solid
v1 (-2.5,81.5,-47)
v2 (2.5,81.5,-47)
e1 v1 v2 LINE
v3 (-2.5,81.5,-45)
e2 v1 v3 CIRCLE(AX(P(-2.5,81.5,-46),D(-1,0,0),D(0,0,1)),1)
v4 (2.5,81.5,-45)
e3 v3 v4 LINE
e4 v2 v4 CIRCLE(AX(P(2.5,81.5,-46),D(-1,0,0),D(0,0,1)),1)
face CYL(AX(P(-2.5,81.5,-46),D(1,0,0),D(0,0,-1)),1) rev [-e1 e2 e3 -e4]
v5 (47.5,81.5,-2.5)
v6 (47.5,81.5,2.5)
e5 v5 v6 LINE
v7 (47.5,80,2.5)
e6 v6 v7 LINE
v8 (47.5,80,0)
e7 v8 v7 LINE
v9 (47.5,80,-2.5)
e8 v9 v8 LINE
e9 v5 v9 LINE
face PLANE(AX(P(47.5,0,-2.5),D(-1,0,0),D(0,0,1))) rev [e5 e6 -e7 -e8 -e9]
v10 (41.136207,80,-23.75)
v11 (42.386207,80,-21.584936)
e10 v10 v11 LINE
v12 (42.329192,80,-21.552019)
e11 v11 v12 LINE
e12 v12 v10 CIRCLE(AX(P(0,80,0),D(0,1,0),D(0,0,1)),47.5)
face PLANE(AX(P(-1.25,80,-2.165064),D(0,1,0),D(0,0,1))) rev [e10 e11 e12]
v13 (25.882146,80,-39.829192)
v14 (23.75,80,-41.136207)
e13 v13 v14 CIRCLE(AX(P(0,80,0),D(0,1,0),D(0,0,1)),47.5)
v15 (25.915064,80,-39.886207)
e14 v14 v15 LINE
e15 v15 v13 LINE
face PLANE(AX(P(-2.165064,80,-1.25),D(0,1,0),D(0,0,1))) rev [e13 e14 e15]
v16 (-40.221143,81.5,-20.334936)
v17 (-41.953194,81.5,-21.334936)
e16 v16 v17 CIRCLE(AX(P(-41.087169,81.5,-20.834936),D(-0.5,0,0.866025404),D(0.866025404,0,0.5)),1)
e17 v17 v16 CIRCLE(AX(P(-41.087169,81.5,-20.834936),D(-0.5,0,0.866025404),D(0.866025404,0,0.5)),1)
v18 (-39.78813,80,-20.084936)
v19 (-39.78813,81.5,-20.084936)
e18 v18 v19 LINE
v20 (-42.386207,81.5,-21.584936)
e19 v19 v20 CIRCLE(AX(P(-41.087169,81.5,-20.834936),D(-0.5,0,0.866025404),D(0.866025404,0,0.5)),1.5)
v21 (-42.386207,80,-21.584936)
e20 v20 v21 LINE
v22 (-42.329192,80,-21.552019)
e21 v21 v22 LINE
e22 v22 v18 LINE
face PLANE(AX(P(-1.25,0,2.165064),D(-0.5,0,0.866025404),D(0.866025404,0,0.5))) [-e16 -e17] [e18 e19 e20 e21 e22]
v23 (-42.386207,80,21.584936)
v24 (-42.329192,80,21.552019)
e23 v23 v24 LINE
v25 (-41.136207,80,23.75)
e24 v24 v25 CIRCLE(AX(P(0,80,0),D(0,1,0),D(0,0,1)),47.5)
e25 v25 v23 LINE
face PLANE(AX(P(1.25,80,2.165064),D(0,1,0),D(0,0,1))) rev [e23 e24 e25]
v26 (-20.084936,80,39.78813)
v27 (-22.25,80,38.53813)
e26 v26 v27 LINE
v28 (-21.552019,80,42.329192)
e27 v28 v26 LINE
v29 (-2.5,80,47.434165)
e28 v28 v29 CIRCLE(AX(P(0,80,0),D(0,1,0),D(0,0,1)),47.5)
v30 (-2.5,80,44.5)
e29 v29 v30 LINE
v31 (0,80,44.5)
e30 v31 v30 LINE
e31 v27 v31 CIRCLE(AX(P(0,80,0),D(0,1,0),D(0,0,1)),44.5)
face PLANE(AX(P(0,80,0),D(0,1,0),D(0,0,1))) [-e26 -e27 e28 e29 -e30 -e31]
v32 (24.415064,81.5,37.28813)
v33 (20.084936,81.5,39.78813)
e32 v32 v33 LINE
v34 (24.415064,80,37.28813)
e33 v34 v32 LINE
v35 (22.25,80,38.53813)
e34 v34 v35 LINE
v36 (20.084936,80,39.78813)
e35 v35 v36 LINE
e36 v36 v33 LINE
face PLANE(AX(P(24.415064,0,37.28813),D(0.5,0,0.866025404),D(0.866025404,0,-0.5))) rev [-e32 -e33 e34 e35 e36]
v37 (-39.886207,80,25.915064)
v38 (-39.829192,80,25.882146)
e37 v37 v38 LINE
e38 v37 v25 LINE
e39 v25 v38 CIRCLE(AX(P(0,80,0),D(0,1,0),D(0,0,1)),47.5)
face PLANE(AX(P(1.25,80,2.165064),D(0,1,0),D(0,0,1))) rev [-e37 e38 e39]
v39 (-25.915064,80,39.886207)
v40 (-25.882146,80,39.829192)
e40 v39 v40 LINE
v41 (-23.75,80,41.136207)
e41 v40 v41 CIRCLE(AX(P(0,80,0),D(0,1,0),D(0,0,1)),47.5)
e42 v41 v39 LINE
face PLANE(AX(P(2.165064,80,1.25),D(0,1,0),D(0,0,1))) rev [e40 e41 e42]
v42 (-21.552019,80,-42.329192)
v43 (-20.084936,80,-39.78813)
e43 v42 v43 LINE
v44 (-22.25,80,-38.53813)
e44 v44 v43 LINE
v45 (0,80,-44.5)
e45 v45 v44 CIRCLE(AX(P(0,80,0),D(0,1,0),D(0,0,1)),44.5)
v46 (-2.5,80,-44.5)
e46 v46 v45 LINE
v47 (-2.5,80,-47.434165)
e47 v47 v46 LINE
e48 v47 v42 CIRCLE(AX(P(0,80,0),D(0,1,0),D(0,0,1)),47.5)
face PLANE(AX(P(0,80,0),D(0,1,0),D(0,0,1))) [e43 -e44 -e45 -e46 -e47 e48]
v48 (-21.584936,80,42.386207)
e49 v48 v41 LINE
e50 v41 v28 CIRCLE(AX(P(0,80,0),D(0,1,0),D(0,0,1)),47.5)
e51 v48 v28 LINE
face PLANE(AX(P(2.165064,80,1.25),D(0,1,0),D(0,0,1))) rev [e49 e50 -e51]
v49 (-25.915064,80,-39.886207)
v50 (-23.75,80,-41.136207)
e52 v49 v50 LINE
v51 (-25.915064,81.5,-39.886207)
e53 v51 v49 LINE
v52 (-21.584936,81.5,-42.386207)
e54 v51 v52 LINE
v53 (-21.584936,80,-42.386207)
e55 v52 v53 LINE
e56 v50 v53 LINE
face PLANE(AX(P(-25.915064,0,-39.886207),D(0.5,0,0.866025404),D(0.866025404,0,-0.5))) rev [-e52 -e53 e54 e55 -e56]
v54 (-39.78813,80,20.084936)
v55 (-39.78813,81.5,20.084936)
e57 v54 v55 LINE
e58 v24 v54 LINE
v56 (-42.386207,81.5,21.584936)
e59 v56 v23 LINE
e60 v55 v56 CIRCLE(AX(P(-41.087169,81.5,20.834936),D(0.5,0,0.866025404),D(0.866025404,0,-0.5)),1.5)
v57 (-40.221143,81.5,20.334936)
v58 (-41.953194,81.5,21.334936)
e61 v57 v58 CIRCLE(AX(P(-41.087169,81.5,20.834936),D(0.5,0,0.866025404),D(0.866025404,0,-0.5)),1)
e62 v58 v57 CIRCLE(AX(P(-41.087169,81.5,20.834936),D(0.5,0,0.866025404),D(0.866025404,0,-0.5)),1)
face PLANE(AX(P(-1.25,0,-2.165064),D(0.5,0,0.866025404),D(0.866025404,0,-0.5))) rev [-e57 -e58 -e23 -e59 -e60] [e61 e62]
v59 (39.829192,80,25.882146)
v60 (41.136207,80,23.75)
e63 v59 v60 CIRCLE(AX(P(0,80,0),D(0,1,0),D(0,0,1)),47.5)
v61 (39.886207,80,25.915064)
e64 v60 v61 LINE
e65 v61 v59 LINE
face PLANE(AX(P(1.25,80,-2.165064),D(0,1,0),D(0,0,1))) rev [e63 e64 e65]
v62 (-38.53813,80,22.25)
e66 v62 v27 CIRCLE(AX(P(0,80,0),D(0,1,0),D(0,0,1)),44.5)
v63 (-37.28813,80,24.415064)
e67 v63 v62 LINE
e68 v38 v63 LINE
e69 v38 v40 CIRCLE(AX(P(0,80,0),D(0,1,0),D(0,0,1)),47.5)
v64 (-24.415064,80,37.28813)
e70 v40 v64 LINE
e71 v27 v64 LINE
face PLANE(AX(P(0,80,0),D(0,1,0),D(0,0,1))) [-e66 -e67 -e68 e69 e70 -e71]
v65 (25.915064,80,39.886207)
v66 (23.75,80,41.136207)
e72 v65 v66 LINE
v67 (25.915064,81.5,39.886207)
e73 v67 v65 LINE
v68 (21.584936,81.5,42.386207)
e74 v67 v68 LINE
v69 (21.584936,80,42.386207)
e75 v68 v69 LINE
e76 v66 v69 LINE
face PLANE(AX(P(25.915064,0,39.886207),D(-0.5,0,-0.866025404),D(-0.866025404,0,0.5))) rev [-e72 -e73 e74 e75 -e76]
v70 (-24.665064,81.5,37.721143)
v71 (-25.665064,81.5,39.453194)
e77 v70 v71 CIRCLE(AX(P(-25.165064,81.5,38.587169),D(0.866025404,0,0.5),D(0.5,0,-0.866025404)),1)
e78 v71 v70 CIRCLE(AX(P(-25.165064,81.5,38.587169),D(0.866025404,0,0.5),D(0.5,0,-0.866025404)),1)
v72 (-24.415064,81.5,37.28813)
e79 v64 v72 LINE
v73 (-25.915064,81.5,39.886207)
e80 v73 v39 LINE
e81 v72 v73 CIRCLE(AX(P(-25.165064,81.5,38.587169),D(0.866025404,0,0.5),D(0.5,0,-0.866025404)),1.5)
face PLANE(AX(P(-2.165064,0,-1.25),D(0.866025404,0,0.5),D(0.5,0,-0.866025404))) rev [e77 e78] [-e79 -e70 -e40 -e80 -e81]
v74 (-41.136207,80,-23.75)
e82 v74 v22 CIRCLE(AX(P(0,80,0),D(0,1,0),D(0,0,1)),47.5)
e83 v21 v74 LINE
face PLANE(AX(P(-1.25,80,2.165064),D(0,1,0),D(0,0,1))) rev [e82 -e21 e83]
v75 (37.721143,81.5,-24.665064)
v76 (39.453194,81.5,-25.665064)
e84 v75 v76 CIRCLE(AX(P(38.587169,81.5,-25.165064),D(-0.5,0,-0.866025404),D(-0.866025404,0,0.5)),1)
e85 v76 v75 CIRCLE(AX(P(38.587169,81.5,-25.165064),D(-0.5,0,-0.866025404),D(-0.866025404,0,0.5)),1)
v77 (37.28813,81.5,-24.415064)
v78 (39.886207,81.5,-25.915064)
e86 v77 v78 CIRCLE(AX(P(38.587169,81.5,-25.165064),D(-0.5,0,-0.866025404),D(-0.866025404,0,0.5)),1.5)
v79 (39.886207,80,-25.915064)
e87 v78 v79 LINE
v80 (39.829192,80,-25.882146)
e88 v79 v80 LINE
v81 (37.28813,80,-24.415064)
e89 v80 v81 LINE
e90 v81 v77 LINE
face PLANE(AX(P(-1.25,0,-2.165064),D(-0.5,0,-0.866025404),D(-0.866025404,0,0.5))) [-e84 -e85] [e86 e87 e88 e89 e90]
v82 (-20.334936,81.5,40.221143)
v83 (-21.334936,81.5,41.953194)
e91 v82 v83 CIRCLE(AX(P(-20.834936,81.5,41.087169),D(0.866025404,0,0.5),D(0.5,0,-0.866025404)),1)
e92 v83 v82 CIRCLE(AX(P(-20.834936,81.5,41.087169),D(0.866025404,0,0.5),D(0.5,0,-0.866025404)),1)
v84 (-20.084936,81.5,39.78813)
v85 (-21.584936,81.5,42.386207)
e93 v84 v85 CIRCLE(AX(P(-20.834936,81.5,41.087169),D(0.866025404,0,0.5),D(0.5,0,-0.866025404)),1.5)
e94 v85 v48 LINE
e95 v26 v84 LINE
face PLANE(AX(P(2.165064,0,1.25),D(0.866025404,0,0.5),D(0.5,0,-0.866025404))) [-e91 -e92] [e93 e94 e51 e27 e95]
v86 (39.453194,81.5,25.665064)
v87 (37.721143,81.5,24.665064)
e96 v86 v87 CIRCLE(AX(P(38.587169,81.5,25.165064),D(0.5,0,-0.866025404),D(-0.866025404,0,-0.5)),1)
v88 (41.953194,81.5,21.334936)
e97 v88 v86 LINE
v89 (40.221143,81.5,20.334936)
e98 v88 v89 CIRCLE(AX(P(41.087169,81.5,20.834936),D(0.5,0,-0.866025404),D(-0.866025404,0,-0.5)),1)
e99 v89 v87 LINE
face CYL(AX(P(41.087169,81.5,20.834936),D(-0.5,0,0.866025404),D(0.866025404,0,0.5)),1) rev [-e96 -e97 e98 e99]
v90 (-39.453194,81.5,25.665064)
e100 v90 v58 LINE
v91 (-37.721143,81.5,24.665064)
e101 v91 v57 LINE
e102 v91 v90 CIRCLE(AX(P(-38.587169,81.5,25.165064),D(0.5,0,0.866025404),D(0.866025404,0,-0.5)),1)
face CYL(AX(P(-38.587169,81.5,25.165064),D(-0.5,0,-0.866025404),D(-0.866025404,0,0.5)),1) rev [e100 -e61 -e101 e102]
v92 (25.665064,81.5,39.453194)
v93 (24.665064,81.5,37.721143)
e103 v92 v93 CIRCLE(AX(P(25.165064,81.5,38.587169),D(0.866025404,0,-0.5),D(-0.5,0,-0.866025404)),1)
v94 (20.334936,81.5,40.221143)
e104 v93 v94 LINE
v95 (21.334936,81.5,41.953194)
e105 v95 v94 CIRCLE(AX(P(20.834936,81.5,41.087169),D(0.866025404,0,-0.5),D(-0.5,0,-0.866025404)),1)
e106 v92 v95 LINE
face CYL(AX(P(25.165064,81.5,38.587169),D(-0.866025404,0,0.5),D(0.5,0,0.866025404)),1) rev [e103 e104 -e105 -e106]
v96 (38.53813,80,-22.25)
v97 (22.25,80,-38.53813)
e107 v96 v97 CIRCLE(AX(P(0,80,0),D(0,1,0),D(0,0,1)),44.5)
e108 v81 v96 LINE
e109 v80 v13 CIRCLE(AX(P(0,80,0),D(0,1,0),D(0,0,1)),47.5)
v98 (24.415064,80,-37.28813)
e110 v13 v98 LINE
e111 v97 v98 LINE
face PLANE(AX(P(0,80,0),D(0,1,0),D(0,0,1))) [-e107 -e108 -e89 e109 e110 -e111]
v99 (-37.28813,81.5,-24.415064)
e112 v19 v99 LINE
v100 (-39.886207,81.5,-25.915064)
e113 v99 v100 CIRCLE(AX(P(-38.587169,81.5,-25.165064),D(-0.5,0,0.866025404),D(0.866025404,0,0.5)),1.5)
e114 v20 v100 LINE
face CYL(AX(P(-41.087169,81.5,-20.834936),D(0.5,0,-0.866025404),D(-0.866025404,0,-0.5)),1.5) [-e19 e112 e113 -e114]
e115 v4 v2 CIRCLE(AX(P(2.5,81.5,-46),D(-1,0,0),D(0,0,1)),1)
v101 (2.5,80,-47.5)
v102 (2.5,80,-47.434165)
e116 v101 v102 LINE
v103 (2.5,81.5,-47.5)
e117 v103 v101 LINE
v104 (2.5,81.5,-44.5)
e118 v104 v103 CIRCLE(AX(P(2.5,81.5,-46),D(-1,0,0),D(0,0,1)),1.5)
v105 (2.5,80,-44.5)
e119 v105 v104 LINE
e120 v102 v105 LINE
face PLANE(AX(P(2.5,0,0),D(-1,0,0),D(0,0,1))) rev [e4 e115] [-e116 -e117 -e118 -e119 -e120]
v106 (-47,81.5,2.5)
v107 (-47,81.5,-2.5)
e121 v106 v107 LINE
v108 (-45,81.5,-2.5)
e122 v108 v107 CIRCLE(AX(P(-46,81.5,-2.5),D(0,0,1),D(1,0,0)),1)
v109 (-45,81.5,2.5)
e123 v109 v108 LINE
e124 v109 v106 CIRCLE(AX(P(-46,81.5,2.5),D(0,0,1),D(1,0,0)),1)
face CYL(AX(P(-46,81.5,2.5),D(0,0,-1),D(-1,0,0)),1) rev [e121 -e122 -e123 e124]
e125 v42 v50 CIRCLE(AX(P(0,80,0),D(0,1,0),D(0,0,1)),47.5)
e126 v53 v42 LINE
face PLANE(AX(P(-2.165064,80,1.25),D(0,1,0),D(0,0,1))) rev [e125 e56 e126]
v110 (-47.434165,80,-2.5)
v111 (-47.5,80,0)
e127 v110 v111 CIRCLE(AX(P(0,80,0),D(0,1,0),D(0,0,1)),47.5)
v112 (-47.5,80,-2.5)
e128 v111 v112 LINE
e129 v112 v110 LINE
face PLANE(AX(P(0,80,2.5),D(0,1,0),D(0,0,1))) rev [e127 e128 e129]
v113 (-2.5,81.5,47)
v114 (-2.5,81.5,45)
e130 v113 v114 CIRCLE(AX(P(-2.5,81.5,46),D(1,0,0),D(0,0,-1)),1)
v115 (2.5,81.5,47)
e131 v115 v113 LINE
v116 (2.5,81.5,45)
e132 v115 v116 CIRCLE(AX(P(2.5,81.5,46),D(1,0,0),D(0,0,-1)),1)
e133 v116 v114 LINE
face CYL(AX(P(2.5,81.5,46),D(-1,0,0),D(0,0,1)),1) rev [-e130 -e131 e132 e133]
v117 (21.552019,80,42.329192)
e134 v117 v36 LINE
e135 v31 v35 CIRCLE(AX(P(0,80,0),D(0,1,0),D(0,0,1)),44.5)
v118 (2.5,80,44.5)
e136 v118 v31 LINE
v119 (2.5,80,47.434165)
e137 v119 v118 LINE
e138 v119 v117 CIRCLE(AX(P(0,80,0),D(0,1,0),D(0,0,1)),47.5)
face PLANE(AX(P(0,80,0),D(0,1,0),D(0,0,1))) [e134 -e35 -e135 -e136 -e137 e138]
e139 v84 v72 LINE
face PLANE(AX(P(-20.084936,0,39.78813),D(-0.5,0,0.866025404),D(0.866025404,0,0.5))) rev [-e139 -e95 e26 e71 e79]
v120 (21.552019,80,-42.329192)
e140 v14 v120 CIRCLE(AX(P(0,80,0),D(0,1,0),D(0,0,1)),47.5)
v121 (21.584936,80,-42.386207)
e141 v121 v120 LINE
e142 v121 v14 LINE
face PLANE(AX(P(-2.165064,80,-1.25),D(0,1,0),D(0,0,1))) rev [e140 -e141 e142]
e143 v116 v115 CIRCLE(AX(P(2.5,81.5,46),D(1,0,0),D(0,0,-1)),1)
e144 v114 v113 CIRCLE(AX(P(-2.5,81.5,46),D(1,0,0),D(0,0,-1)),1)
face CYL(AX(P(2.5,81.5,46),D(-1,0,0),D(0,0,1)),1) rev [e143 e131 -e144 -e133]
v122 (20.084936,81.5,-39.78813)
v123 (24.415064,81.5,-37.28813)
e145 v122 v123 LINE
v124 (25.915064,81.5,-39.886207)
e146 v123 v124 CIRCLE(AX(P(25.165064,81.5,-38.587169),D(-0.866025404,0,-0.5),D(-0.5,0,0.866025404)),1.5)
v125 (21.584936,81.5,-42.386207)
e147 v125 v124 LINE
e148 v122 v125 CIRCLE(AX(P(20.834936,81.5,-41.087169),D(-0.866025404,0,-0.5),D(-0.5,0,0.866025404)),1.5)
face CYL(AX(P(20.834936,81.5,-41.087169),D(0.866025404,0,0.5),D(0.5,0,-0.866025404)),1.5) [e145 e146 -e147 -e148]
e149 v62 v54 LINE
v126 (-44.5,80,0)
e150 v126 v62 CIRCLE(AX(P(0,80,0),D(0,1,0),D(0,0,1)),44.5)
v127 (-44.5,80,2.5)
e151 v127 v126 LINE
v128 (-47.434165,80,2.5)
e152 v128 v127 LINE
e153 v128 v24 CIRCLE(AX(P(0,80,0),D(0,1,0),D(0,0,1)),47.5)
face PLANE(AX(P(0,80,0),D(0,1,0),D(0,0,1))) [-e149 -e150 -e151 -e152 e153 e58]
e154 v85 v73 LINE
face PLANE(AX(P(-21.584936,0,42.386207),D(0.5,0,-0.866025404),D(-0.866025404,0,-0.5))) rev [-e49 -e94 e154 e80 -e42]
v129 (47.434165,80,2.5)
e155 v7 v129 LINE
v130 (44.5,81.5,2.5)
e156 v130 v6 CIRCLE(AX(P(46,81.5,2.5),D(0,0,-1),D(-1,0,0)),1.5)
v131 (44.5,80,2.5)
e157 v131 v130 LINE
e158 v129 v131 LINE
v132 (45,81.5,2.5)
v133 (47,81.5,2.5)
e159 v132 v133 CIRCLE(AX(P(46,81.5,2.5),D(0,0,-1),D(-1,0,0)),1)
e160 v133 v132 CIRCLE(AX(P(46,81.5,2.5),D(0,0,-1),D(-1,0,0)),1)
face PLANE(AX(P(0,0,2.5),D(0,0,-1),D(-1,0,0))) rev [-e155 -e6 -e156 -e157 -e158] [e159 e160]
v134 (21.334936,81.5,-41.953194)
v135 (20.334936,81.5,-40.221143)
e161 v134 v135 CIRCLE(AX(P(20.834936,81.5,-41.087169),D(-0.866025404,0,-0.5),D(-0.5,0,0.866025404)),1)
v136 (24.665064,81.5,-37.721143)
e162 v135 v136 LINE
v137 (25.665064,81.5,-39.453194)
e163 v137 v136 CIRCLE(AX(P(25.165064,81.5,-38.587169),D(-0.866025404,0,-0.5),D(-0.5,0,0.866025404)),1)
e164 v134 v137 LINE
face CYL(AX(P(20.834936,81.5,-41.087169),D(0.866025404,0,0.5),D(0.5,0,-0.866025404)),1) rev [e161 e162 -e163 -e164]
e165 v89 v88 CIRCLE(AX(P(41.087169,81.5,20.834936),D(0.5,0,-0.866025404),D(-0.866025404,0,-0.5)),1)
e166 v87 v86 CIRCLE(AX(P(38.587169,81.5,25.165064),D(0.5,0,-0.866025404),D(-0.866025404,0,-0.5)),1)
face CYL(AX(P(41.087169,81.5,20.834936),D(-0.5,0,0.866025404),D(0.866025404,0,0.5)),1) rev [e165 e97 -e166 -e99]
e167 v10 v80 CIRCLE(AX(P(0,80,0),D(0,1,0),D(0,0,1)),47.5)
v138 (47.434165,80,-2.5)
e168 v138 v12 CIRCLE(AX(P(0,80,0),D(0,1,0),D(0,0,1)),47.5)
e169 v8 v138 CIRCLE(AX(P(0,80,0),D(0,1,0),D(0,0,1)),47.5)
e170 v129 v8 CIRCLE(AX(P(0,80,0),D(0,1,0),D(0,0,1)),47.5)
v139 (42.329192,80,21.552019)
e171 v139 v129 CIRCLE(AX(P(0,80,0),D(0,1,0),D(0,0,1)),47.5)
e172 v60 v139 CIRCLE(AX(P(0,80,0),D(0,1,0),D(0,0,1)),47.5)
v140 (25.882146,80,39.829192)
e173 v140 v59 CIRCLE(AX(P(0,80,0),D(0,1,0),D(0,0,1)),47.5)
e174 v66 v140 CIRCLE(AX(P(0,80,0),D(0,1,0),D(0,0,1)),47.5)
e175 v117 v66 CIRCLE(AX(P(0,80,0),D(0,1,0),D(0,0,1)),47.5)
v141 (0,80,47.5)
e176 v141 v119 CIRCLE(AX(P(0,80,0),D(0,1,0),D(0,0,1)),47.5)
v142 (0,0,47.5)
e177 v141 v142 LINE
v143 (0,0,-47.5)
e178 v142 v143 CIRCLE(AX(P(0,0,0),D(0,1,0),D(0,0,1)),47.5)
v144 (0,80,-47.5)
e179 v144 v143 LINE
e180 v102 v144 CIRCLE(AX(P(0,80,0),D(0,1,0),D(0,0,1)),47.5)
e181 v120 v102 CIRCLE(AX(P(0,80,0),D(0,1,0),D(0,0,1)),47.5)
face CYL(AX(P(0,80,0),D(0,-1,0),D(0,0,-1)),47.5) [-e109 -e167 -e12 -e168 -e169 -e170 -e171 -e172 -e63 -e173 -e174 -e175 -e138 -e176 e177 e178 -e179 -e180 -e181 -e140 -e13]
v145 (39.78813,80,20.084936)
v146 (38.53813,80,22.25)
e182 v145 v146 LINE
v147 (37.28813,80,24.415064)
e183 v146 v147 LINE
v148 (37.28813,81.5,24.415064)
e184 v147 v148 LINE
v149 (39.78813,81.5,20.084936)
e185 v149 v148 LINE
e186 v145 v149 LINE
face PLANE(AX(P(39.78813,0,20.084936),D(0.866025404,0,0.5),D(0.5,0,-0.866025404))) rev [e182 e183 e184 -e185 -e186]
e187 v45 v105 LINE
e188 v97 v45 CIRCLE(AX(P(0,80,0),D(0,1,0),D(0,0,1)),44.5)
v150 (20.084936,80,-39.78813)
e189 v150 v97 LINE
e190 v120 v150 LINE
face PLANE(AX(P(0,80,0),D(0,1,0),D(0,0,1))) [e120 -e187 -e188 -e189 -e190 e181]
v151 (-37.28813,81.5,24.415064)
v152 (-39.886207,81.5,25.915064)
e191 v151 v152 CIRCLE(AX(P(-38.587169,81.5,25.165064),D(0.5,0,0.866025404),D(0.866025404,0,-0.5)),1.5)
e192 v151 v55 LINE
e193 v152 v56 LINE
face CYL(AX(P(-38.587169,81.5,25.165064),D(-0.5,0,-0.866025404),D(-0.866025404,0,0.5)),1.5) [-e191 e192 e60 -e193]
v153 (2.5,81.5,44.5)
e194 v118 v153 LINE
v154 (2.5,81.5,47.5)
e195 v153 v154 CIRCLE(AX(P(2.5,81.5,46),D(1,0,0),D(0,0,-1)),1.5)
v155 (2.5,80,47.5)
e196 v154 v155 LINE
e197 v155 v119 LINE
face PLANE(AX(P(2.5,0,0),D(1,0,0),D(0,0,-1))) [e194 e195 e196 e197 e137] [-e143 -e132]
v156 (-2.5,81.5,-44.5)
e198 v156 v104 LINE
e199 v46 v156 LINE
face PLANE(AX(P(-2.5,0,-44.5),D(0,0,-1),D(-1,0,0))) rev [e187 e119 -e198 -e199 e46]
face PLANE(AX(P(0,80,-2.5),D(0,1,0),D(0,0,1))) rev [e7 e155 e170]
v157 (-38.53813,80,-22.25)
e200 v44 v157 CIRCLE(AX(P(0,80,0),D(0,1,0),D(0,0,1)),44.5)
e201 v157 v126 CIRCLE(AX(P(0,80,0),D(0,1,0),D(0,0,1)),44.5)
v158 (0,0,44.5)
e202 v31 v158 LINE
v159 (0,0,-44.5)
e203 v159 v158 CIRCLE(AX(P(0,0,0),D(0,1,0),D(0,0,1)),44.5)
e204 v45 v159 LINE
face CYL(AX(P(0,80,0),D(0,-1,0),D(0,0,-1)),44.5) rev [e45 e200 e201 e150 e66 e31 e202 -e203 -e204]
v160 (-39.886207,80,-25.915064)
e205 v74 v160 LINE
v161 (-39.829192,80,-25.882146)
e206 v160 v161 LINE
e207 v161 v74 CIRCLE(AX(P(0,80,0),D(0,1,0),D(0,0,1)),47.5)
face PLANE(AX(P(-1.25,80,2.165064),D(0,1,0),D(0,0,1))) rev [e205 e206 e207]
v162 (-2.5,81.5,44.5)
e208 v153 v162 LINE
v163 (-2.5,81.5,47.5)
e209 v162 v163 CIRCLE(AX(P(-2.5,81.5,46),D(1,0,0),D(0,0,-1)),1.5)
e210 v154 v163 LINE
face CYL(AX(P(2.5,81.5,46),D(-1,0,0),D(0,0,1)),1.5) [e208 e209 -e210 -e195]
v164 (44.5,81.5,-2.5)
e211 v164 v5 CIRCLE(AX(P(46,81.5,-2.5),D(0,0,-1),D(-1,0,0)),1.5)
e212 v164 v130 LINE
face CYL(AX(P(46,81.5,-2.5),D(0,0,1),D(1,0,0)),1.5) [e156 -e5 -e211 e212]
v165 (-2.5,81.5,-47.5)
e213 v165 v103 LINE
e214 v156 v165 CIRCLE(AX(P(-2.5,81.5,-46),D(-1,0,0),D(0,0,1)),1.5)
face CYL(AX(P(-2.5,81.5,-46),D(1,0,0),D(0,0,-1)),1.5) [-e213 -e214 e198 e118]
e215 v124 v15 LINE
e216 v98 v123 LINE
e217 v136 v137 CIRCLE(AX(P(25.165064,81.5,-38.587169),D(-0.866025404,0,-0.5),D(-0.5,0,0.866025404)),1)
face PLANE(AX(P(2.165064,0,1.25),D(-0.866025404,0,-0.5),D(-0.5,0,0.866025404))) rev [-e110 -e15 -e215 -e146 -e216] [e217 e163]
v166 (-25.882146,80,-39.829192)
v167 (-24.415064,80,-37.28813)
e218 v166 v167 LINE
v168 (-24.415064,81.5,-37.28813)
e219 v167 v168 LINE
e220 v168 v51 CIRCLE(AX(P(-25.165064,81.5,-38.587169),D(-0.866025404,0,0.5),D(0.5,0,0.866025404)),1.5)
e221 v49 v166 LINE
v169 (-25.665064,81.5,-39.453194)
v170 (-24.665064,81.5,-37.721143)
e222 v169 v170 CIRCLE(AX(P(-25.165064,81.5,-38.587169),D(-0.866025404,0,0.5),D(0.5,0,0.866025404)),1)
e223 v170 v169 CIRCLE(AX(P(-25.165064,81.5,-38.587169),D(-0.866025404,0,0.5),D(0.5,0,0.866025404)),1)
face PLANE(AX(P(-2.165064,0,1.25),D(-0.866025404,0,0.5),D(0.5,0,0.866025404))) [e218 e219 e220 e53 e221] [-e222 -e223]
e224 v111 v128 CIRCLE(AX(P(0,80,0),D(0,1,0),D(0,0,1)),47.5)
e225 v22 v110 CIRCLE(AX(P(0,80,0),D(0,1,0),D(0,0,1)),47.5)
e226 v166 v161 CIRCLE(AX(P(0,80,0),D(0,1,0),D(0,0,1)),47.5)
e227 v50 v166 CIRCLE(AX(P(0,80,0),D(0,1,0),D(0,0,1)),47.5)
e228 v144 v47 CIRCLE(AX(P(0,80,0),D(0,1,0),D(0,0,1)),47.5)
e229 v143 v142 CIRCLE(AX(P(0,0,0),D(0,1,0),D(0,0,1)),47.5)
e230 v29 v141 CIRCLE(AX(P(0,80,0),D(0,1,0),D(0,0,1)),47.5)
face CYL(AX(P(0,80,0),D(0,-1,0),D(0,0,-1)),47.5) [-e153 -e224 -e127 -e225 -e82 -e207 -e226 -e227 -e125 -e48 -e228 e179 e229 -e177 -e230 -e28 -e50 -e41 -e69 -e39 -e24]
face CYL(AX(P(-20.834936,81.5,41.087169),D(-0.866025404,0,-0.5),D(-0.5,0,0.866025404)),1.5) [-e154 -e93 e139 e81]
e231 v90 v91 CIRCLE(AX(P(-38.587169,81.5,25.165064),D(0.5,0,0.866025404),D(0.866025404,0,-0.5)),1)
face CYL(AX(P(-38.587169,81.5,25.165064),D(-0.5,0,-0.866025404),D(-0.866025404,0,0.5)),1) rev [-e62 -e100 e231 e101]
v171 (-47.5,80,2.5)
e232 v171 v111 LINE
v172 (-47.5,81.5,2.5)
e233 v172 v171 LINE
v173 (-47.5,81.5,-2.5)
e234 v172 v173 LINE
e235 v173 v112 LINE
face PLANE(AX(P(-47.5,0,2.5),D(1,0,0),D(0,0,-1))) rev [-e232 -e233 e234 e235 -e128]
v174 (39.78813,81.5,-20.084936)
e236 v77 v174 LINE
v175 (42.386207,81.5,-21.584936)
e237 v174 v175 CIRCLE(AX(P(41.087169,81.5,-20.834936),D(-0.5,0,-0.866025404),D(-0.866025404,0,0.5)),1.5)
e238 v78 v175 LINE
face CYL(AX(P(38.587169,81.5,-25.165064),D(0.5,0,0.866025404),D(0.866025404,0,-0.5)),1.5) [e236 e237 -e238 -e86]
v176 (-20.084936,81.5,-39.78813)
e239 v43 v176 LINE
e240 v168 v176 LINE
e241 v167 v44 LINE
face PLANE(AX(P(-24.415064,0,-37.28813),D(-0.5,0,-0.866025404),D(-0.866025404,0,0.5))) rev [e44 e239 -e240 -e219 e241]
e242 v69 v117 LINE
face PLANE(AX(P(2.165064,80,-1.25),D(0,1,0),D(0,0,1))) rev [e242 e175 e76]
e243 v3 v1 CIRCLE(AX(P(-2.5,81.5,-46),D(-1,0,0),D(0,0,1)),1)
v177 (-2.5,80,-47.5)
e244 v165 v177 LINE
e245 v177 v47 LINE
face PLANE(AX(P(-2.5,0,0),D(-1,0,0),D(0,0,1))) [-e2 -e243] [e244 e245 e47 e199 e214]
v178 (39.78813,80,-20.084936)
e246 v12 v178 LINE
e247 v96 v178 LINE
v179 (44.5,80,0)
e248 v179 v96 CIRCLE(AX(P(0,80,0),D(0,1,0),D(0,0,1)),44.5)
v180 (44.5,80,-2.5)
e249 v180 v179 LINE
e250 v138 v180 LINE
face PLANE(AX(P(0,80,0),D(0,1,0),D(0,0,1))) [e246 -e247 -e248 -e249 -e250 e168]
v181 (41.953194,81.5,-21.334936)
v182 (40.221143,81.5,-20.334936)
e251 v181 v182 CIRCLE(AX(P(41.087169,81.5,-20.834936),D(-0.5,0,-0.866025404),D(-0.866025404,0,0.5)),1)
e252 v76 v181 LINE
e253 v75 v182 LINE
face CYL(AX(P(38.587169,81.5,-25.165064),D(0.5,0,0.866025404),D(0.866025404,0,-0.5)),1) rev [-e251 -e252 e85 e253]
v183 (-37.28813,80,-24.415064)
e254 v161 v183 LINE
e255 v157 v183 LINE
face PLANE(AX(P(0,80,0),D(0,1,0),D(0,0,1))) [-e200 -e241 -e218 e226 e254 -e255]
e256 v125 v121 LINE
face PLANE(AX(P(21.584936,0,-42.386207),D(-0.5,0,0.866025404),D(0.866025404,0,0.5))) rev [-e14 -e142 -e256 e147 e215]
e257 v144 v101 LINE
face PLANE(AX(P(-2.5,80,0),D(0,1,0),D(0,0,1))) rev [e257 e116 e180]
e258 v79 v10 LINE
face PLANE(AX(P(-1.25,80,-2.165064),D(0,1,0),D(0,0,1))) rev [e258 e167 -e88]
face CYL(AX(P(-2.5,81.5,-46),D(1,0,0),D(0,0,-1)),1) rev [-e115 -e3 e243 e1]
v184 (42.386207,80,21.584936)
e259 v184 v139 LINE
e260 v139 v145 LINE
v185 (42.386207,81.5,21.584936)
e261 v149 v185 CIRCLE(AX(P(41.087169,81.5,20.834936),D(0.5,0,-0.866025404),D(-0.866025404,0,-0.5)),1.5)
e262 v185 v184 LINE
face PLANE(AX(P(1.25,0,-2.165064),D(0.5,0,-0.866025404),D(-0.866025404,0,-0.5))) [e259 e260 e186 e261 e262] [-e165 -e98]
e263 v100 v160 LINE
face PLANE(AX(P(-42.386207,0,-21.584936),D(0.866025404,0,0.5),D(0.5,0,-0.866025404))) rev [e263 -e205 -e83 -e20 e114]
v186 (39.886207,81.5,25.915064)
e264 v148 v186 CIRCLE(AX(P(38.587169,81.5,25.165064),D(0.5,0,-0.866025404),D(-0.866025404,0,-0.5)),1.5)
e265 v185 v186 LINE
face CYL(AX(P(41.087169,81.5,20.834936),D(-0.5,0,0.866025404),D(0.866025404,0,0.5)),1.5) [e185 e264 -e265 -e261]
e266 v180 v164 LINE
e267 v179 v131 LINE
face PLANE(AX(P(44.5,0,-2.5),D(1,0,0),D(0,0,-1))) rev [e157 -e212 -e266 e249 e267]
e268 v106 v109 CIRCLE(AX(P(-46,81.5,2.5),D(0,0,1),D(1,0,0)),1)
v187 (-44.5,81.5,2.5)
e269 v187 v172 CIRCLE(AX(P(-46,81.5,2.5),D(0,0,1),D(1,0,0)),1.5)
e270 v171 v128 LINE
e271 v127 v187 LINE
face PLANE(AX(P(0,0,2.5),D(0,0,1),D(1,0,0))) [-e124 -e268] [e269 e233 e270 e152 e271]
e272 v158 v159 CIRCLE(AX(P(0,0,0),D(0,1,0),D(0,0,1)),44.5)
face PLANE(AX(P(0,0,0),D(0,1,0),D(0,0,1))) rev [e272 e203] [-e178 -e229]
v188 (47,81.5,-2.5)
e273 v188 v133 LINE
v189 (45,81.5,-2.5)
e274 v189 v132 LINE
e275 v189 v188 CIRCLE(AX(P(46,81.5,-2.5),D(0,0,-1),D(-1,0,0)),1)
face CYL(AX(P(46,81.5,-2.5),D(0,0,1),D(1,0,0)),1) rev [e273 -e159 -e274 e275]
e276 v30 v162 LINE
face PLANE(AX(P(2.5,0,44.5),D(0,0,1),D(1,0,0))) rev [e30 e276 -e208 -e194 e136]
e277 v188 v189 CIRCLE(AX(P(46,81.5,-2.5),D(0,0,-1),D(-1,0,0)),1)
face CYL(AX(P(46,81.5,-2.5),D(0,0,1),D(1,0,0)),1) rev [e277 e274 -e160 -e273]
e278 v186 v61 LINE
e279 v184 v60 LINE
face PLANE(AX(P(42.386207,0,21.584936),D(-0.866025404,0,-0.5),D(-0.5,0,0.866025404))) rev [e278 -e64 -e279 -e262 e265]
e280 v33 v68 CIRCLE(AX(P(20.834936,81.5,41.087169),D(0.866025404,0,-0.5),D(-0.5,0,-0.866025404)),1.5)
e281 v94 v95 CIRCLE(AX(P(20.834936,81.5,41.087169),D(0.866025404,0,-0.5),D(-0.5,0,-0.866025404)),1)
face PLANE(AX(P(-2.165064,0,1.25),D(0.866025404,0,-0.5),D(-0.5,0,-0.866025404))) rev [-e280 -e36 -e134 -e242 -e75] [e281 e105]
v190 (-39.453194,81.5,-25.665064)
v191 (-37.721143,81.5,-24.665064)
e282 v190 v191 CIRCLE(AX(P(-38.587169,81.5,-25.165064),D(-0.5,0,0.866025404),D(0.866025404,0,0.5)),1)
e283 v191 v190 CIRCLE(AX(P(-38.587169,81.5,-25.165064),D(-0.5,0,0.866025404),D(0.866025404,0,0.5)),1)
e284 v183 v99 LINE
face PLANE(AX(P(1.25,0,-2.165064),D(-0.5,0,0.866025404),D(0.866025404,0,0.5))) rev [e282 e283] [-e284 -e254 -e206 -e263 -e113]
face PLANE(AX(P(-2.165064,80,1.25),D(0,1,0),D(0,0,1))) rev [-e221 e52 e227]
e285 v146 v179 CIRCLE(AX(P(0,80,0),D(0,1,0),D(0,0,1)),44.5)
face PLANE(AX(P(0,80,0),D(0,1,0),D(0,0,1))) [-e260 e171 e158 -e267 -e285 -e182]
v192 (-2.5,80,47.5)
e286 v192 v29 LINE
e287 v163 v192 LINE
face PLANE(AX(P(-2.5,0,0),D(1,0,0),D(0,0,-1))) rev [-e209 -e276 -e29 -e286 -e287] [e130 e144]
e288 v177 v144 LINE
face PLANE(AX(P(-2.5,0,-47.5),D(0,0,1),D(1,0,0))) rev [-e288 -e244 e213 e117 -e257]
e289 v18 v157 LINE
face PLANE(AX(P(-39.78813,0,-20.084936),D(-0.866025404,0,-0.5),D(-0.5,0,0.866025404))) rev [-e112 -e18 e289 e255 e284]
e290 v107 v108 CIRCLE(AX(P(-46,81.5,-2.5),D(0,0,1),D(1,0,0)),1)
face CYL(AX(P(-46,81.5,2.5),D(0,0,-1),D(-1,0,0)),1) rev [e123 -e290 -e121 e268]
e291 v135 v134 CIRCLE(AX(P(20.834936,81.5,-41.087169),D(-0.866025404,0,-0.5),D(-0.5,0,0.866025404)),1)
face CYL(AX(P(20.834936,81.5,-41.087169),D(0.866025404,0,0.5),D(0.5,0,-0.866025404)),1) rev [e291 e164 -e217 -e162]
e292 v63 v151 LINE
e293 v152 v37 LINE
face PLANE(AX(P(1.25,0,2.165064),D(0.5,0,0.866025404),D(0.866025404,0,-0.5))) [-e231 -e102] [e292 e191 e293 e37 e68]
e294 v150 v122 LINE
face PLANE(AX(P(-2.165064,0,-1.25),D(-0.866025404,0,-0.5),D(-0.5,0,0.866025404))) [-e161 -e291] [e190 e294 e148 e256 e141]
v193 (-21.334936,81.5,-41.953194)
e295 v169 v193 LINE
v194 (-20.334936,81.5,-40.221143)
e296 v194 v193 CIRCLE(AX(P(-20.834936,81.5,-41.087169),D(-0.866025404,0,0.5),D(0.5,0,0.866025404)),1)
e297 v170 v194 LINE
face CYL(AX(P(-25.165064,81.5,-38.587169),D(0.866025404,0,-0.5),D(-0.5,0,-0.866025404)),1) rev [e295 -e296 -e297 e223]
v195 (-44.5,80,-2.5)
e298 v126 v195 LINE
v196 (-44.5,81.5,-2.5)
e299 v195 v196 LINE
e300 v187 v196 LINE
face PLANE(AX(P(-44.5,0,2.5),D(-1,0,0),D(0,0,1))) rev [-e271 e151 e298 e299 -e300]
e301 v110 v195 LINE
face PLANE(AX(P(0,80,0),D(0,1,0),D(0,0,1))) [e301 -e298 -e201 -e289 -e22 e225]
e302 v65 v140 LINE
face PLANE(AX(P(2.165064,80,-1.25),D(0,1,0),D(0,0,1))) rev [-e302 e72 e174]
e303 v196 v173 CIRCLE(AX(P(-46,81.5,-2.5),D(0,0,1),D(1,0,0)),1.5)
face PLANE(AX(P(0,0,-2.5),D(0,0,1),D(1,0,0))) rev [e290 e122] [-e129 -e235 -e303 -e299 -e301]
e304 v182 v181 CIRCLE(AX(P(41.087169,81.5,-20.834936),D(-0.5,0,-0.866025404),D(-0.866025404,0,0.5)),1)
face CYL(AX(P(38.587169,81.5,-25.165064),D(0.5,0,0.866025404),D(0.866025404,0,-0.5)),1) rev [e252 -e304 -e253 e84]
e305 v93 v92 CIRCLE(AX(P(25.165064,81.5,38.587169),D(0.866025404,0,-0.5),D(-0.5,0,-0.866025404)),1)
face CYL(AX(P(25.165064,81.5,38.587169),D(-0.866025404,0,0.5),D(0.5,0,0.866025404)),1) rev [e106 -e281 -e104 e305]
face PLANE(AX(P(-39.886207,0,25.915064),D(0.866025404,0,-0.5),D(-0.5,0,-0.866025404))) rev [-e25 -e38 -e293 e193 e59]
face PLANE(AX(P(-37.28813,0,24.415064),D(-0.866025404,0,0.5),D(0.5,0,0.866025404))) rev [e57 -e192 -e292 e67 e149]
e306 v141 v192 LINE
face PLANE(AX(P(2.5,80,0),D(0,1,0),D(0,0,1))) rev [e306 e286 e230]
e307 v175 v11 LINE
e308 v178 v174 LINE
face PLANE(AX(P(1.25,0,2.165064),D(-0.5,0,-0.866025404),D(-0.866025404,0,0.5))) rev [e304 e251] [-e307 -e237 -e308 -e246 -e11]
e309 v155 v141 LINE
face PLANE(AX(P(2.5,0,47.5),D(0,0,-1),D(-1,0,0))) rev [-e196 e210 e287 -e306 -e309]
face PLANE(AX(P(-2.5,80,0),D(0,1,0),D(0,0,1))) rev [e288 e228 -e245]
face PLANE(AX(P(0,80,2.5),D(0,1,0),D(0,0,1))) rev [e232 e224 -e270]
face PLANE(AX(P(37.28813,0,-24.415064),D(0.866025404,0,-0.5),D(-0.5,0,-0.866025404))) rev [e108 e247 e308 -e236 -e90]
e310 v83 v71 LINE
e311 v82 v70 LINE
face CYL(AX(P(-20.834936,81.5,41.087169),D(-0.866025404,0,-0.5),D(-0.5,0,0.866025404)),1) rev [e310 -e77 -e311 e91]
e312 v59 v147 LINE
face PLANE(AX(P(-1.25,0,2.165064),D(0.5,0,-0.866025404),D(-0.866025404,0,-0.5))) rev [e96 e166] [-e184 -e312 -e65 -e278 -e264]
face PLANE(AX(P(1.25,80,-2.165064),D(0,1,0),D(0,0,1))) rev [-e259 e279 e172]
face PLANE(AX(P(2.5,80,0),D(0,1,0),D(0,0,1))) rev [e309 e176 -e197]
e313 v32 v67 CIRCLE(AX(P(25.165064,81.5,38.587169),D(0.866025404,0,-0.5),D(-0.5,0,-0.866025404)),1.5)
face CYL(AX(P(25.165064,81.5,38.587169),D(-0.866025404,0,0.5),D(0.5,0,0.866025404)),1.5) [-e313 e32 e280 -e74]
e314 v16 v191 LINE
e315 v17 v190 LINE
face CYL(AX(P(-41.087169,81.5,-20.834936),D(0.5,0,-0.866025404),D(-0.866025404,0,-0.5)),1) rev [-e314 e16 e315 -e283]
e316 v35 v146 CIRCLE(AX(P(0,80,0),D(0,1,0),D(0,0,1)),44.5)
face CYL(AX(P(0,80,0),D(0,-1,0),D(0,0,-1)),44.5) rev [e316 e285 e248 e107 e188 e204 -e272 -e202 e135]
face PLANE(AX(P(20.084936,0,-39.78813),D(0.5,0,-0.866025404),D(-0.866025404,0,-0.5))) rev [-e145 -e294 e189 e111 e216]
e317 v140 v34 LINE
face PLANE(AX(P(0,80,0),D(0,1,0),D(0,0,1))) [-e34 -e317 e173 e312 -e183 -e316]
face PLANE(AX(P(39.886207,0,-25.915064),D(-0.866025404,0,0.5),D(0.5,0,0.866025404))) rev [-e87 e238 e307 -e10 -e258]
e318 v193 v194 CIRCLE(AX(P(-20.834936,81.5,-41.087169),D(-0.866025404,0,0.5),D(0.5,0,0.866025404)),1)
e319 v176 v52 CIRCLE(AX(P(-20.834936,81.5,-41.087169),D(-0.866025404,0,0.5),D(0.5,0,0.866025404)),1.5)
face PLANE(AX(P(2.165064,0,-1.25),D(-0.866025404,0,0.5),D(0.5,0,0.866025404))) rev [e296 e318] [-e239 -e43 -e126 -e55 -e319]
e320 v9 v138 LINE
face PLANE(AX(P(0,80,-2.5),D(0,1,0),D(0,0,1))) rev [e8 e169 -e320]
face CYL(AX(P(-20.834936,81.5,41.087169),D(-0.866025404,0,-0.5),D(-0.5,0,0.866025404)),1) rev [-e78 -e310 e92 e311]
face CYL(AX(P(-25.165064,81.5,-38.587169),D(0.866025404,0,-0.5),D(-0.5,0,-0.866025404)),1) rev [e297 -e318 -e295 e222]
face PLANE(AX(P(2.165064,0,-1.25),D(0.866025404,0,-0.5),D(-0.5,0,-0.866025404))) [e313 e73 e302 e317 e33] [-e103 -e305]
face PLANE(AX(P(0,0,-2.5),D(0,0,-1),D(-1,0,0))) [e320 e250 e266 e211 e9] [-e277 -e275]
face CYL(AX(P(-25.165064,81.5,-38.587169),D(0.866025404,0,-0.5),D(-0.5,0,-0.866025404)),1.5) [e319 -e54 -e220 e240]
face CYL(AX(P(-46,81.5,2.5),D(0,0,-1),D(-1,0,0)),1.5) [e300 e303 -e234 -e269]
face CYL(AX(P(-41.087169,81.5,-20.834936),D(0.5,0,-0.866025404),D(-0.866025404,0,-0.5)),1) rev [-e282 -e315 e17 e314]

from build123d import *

# Parameters (mm, degrees)
SKETCH_1_R               = 47.5
SKETCH_1_R_2             = 44.5
EXTRUDE_1_DEPTH          = 80
SKETCH_2_R               = 1.5
SKETCH_2_R_2             = 1
EXTRUDE_3_DEPTH          = 2.5
PATTERN_CIRCULAR_1_COUNT = 12


with BuildPart() as part:
    # 草图1 → 凸台-拉伸1 (new body)
    with BuildSketch(Plane(origin=(0, 0, 0), x_dir=(1, 0, 0), z_dir=(0, 1, 0))):
        with Locations(Location((0, 0, 0), (0, 0, 270))):
            Circle(SKETCH_1_R)
        with Locations(Location((0, 0, 0), (0, 0, 270))):
            Circle(SKETCH_1_R_2, mode=Mode.SUBTRACT)
    extrude(amount=EXTRUDE_1_DEPTH)

    # 草图2 → 凸台-拉伸3 (add, symmetric)
    # profile 1 of 3: a face of its own
    with BuildSketch(Plane(origin=(0, 0, 0), x_dir=(0, 0, -1), z_dir=(1, 0, 0))):
        with BuildLine():
            ThreePointArc((-46, 80), (-47.060660172, 80.439339828), (-47.5, 81.5))
            Line((-47.5, 81.5), (-47.5, 80))
            Line((-47.5, 80), (-46, 80))
        make_face()
    # profile 2 of 3: a face of its own
    with BuildSketch(Plane(origin=(0, 0, 0), x_dir=(0, 0, -1), z_dir=(1, 0, 0))):
        with BuildLine():
            Line((-44.5, 80), (-44.5, 81.5))
            ThreePointArc((-44.5, 81.5), (-44.939339828, 80.439339828), (-46, 80))
            Line((-46, 80), (-44.5, 80))
        make_face()
    # profile 3 of 3: a face of its own
    with BuildSketch(Plane(origin=(0, 0, 0), x_dir=(0, 0, -1), z_dir=(1, 0, 0))):
        with Locations((-46, 81.5)):
            Circle(SKETCH_2_R)
        with Locations((-46, 81.5)):
            Circle(SKETCH_2_R_2, mode=Mode.SUBTRACT)
    extrude_3 = extrude(amount=EXTRUDE_3_DEPTH, both=True)

    # 阵列(圆周)1: 凸台-拉伸3 ×12 about axis
    pattern_circular_1_axis = Axis((0, 0, 0), (0, 1, 0))
    for i in range(1, PATTERN_CIRCULAR_1_COUNT):
        add(extrude_3.rotate(pattern_circular_1_axis, i * 360 / PATTERN_CIRCULAR_1_COUNT))


solid = part.part
